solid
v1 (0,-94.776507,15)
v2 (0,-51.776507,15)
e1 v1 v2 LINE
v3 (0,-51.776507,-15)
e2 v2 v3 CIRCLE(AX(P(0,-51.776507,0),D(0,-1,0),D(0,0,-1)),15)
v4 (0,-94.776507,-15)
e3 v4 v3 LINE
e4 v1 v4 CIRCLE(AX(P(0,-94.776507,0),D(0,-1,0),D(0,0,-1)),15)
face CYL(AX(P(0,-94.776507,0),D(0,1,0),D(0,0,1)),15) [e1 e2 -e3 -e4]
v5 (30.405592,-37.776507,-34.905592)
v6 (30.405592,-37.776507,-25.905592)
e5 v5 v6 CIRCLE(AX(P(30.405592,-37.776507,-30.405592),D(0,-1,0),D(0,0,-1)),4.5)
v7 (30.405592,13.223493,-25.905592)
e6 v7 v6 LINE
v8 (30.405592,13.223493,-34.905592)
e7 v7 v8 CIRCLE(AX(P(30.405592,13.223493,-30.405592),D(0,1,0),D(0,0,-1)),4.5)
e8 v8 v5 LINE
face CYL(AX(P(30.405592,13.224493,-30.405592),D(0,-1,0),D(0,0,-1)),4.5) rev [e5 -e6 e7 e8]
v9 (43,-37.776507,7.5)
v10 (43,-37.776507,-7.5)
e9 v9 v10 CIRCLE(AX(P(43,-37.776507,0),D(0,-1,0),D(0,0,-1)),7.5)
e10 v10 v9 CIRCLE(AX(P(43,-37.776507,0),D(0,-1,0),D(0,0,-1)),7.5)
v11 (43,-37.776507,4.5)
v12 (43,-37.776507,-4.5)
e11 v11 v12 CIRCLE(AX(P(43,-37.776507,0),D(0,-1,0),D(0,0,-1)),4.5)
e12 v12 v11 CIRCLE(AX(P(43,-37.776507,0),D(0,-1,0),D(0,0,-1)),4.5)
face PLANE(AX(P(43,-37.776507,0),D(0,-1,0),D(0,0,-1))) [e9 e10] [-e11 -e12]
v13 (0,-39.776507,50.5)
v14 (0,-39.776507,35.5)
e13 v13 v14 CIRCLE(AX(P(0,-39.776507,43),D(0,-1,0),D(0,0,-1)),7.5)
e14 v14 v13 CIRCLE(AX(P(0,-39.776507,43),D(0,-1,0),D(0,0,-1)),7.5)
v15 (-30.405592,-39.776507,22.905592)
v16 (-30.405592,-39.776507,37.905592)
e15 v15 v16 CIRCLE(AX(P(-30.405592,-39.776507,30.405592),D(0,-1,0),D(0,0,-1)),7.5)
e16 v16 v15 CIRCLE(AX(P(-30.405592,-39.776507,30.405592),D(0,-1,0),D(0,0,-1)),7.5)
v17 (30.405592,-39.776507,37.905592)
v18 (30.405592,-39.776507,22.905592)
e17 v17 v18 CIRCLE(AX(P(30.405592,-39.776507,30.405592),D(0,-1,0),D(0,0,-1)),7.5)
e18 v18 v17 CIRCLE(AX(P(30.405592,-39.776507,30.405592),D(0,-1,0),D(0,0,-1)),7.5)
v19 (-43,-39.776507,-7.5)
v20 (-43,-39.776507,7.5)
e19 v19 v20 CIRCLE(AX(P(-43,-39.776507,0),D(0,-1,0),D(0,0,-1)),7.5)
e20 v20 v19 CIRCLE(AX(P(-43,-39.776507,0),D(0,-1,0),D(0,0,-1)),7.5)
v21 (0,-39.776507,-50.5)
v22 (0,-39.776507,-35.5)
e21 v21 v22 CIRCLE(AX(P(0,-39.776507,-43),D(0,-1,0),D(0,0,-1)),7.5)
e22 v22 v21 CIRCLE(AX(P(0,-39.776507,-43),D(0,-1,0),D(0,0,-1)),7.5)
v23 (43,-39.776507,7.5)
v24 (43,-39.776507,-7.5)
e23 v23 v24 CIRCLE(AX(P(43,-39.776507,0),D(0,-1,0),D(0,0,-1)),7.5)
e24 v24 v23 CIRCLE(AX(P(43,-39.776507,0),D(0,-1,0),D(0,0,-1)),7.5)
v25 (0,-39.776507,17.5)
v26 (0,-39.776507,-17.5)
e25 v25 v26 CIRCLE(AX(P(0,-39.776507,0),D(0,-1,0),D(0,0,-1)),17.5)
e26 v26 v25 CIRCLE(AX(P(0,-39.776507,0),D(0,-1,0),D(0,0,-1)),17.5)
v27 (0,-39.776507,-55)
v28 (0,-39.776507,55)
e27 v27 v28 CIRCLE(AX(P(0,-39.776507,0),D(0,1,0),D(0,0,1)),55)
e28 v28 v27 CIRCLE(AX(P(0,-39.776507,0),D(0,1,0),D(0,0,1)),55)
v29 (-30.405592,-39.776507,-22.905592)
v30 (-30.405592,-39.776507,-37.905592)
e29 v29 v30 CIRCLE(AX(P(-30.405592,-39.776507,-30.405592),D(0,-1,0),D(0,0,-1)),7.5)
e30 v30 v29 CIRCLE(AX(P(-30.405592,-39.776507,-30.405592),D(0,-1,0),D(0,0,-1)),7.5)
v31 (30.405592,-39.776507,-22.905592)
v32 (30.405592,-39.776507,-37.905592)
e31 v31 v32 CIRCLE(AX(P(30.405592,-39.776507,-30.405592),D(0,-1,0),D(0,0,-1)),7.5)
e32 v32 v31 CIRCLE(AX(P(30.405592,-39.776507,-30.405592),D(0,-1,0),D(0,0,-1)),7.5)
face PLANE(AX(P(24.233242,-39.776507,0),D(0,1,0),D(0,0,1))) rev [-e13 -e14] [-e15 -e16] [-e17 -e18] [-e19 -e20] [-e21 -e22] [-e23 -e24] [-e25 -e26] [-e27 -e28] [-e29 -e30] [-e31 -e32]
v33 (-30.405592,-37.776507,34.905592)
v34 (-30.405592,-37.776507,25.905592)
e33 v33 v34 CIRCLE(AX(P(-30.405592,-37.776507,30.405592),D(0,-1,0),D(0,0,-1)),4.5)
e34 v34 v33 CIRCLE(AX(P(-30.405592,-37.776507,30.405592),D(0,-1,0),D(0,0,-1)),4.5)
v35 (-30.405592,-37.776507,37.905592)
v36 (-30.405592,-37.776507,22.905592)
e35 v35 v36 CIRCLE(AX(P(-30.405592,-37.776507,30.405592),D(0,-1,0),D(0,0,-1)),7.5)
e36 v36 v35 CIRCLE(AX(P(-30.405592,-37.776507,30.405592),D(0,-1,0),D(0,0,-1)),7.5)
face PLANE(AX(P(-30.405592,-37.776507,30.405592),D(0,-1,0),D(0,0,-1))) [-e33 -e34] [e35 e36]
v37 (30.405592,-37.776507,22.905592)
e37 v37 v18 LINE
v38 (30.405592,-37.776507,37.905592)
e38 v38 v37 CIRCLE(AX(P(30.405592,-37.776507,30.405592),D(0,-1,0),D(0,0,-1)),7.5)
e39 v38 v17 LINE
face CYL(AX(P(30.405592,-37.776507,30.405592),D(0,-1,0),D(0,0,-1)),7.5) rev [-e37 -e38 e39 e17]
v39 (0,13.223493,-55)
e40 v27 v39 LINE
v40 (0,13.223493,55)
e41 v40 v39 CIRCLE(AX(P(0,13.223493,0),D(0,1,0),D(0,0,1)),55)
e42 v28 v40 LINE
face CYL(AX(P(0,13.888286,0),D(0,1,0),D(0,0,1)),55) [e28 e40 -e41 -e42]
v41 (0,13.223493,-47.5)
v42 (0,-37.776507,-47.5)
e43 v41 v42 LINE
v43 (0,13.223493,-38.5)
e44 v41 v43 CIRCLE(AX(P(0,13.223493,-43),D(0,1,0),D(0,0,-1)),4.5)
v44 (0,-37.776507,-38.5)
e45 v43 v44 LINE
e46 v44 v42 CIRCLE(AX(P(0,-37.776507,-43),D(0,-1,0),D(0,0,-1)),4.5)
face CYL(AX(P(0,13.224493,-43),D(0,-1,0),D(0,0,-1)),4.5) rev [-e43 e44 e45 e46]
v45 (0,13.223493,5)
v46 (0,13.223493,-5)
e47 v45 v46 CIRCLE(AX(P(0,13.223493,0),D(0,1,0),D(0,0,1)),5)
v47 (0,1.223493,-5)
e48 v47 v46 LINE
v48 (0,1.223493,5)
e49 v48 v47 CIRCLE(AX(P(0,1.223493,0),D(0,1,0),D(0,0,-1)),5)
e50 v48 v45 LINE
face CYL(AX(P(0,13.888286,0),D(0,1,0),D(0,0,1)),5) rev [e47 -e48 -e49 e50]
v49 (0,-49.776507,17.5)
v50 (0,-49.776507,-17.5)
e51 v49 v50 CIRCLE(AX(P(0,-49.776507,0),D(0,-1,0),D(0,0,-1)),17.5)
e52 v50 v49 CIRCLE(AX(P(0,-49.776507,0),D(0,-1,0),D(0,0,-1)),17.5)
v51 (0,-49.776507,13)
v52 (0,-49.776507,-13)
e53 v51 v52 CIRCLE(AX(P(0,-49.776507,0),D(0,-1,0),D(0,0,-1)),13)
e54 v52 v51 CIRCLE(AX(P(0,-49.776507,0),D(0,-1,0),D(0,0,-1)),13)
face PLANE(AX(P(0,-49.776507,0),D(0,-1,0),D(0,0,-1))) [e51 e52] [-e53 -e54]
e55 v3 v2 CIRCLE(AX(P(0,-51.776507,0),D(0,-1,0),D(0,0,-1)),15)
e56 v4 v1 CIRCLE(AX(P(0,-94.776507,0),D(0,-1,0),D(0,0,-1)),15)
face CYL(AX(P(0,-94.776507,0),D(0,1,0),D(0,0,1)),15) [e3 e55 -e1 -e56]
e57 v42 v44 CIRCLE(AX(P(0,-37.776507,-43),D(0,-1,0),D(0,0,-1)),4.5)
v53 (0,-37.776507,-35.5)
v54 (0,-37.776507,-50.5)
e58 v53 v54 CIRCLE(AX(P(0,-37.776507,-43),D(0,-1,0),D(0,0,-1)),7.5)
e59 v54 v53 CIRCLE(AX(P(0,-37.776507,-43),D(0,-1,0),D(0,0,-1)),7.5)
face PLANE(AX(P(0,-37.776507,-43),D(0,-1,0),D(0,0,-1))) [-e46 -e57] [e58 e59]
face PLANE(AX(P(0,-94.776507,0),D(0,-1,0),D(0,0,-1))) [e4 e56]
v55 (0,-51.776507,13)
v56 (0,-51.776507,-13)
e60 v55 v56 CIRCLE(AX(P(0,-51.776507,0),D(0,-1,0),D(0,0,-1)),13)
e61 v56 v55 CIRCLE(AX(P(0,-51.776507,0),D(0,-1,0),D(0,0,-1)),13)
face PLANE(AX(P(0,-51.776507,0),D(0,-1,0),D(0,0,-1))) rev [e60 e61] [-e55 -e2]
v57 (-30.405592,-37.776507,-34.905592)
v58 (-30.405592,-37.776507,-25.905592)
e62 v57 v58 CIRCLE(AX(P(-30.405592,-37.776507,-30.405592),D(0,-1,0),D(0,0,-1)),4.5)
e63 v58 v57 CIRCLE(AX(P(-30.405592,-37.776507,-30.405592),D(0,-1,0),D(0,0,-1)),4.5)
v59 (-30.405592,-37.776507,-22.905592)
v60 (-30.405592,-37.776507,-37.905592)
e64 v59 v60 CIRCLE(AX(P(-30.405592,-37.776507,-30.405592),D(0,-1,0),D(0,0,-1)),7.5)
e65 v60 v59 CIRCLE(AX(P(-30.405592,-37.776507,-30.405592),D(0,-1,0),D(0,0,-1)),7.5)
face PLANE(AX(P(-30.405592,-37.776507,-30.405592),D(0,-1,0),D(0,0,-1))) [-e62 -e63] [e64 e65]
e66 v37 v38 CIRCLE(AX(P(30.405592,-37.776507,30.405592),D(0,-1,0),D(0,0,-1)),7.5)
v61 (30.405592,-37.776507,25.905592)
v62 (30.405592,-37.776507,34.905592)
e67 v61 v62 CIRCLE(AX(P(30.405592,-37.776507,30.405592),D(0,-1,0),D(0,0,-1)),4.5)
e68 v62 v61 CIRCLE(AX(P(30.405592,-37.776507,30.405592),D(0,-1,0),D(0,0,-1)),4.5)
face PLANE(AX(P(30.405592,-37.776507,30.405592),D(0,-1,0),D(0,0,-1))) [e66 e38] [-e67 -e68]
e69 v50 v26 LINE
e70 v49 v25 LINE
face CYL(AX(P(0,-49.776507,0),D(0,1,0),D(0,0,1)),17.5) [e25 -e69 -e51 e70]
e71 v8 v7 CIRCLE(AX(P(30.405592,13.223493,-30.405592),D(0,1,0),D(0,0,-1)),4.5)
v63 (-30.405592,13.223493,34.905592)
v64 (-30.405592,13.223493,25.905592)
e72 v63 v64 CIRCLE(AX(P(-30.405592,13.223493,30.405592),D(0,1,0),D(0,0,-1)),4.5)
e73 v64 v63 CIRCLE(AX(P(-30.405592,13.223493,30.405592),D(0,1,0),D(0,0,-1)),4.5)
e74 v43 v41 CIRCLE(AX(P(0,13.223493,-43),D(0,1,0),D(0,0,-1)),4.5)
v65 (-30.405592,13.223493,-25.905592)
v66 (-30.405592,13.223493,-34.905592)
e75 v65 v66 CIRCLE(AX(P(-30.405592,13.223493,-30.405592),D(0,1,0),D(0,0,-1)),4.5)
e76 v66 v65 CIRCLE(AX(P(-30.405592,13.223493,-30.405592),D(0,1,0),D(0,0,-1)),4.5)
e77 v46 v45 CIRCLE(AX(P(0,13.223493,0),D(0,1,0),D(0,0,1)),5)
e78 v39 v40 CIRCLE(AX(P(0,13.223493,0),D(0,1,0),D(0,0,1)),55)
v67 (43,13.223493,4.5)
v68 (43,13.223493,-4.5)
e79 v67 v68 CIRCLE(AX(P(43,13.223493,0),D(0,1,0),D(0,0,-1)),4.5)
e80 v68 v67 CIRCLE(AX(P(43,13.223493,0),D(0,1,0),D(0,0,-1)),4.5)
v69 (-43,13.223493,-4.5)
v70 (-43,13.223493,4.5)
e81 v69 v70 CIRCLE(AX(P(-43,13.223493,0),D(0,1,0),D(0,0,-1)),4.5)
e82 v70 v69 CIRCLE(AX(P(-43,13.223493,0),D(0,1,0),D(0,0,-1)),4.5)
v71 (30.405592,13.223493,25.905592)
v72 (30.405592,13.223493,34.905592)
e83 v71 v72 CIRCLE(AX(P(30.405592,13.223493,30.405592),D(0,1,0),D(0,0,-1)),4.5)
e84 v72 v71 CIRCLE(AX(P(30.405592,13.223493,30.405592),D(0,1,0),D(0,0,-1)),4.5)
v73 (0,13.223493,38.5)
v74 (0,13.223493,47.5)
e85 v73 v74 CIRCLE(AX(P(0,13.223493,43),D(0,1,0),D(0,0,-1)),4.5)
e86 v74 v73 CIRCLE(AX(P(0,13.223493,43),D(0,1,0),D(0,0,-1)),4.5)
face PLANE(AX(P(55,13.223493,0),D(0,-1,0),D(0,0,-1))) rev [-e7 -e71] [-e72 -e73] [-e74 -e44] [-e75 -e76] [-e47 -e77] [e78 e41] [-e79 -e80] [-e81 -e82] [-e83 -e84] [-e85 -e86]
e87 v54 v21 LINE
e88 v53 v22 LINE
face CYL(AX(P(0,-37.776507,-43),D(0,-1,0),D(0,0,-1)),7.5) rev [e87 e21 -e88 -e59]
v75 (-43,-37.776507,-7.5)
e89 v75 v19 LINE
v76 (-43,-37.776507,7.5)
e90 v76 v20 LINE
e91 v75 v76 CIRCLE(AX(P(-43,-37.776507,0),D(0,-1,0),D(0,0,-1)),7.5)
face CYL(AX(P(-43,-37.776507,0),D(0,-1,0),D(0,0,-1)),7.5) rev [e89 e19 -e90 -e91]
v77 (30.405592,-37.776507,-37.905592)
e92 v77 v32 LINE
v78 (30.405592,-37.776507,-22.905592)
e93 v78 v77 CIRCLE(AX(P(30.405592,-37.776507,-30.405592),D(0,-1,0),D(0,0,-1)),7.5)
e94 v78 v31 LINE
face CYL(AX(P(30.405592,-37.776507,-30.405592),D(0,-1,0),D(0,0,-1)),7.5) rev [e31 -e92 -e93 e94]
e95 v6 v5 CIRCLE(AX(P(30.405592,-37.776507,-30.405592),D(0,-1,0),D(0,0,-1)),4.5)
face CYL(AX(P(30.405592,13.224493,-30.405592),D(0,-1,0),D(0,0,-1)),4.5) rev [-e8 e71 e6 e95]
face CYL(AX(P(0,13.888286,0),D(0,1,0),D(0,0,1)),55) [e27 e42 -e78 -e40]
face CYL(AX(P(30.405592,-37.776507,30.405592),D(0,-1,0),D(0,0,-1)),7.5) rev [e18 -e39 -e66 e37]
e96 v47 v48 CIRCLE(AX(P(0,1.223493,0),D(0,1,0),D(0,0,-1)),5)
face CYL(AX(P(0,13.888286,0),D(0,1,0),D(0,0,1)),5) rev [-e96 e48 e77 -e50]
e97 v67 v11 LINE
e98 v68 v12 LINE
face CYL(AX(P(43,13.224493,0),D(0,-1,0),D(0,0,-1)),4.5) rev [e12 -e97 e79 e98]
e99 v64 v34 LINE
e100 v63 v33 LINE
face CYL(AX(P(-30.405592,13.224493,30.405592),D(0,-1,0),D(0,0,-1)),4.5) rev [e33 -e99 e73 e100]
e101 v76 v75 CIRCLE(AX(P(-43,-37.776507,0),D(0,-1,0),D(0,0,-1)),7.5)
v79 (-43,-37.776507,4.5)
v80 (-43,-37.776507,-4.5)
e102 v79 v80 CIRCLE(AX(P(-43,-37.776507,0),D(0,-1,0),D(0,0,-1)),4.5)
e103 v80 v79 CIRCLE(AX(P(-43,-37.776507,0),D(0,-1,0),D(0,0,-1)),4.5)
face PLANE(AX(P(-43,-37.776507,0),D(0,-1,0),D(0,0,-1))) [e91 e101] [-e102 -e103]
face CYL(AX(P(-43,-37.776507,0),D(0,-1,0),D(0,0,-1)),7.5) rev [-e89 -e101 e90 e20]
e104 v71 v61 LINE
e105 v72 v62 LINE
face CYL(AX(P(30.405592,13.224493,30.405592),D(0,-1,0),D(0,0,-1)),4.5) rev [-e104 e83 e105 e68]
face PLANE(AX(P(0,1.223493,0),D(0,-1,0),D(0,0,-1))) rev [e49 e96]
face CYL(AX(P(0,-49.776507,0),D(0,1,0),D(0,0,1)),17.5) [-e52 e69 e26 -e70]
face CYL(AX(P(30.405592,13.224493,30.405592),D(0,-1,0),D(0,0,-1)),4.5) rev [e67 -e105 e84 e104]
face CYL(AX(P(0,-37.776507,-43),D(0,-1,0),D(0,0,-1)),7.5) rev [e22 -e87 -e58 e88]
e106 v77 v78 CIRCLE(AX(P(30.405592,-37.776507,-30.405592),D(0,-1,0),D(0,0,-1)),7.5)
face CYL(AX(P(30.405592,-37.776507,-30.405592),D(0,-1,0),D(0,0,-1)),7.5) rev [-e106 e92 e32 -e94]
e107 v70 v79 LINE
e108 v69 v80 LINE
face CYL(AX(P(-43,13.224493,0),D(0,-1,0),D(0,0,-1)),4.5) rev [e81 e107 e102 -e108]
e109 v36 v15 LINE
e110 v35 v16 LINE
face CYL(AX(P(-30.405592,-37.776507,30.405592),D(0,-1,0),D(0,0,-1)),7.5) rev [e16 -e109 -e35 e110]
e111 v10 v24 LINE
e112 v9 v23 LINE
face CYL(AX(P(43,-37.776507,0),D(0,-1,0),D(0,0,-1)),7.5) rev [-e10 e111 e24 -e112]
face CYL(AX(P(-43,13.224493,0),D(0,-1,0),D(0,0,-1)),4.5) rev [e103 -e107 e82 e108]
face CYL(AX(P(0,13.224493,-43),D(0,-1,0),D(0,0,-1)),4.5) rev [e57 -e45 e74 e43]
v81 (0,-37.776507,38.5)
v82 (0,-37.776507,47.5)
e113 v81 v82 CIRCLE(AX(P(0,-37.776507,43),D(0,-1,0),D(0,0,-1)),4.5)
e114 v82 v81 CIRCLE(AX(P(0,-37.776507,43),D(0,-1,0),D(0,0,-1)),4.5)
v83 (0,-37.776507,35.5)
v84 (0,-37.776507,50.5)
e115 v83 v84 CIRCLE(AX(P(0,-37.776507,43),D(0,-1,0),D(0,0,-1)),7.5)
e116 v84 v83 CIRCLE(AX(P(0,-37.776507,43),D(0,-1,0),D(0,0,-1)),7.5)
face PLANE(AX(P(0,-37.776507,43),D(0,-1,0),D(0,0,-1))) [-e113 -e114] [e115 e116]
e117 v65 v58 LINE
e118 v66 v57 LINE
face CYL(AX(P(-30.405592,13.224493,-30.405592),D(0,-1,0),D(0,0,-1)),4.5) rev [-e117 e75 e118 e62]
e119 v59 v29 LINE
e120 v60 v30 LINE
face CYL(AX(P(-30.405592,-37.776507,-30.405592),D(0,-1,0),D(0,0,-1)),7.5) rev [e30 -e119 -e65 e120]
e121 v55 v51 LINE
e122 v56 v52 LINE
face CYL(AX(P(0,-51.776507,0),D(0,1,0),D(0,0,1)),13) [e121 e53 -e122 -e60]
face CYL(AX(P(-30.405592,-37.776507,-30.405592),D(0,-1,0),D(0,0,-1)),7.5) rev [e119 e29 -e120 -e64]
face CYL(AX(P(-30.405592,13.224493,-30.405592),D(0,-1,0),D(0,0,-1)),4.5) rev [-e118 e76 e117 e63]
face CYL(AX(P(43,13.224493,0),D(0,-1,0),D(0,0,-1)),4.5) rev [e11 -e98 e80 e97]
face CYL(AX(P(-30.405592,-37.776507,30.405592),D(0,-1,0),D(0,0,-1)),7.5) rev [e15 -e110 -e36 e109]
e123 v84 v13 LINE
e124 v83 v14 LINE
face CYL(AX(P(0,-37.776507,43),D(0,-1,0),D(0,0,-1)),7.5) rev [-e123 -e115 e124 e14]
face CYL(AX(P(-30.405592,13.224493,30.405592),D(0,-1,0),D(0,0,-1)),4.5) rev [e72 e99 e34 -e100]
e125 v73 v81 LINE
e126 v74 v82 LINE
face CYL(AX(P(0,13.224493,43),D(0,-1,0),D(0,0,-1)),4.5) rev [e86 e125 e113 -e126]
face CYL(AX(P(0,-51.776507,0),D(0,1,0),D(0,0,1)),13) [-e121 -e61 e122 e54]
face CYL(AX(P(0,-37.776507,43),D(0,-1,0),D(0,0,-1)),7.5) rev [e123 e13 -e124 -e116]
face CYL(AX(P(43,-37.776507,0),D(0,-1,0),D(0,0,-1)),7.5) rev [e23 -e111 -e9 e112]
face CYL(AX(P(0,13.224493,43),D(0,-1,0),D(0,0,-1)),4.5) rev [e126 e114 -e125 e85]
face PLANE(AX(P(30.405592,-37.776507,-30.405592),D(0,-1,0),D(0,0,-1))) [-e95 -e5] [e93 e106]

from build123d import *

# Parameters (mm, degrees)
SKETCH_2_R          = 7.5
CUT_EXTRUDE_1_DEPTH = 2
CUT_EXTRUDE_2_REACH = 95.011
SKETCH_5_R          = 4.5
SKETCH_7_R          = 30.721623485
EXTRUDE_1_DEPTH     = 41
SKETCH_8_R          = 17.5
EXTRUDE_2_DEPTH     = 10
SKETCH_9_R          = 15
EXTRUDE_3_DEPTH     = 45
SKETCH_10_R         = 15
SKETCH_10_R_2       = 13
CUT_EXTRUDE_3_DEPTH = 2


with BuildPart() as part:
    # 草图1 → 旋转1 (revolve)
    with BuildSketch(Plane.XY, mode=Mode.PRIVATE) as revolve_1_sk:
        with BuildLine():
            Line((5, 13.223493336), (5, 0.265127902))
            ThreePointArc((5, 0.265127902), (24.788681465, -14.86973249), (24.233241632, -39.776506664))
            Line((24.233241632, -39.776506664), (55, -39.776506664))
            Line((55, -39.776506664), (55, 13.223493336))
            Line((55, 13.223493336), (5, 13.223493336))
        make_face()
    revolve(revolve_1_sk.sketch.rotate(Axis((0, 13.888286008, 0), (0, -1, 0)), 90), axis=Axis((0, 13.888286008, 0), (0, -1, 0)))

    # 草图2 → 切除-拉伸1 (cut)
    with BuildSketch(Plane.XZ.offset(39.776506664)):
        with Locations(Location((43, 0, 0), (0, 0, 270))):
            Circle(SKETCH_2_R)
        with Locations(Location((30.405591591, -30.405591591, 0), (0, 0, 270))):
            Circle(SKETCH_2_R)
        with Locations(Location((0, -43, 0), (0, 0, 270))):
            Circle(SKETCH_2_R)
        with Locations(Location((-30.405591591, -30.405591591, 0), (0, 0, 270))):
            Circle(SKETCH_2_R)
        with Locations(Location((-43, 0, 0), (0, 0, 270))):
            Circle(SKETCH_2_R)
        with Locations(Location((-30.405591591, 30.405591591, 0), (0, 0, 270))):
            Circle(SKETCH_2_R)
        with Locations(Location((0, 43, 0), (0, 0, 270))):
            Circle(SKETCH_2_R)
        with Locations(Location((30.405591591, 30.405591591, 0), (0, 0, 270))):
            Circle(SKETCH_2_R)
    extrude(amount=-CUT_EXTRUDE_1_DEPTH, mode=Mode.SUBTRACT)

    # 草图5 → 切除-拉伸2 (cut, up to next)
    with BuildSketch(Plane.XZ.offset(37.776506664), mode=Mode.PRIVATE) as cut_extrude_2_sk1:
        with Locations(Location((0, 43, 0), (0, 0, 270))):
            Circle(SKETCH_5_R)
    cut_extrude_2_tool1 = extrude(cut_extrude_2_sk1.sketch, amount=-CUT_EXTRUDE_2_REACH, mode=Mode.PRIVATE) & part.part
    # 草图5 → 切除-拉伸2 (cut, up to next)
    with BuildSketch(Plane.XZ.offset(37.776506664), mode=Mode.PRIVATE) as cut_extrude_2_sk2:
        with Locations(Location((30.405591591, 30.405591591, 0), (0, 0, 270))):
            Circle(SKETCH_5_R)
    cut_extrude_2_tool2 = extrude(cut_extrude_2_sk2.sketch, amount=-CUT_EXTRUDE_2_REACH, mode=Mode.PRIVATE) & part.part
    # 草图5 → 切除-拉伸2 (cut, up to next)
    with BuildSketch(Plane.XZ.offset(37.776506664), mode=Mode.PRIVATE) as cut_extrude_2_sk3:
        with Locations(Location((43, 0, 0), (0, 0, 270))):
            Circle(SKETCH_5_R)
    cut_extrude_2_tool3 = extrude(cut_extrude_2_sk3.sketch, amount=-CUT_EXTRUDE_2_REACH, mode=Mode.PRIVATE) & part.part
    # 草图5 → 切除-拉伸2 (cut, up to next)
    with BuildSketch(Plane.XZ.offset(37.776506664), mode=Mode.PRIVATE) as cut_extrude_2_sk4:
        with Locations(Location((30.405591591, -30.405591591, 0), (0, 0, 270))):
            Circle(SKETCH_5_R)
    cut_extrude_2_tool4 = extrude(cut_extrude_2_sk4.sketch, amount=-CUT_EXTRUDE_2_REACH, mode=Mode.PRIVATE) & part.part
    # 草图5 → 切除-拉伸2 (cut, up to next)
    with BuildSketch(Plane.XZ.offset(37.776506664), mode=Mode.PRIVATE) as cut_extrude_2_sk5:
        with Locations(Location((0, -43, 0), (0, 0, 270))):
            Circle(SKETCH_5_R)
    cut_extrude_2_tool5 = extrude(cut_extrude_2_sk5.sketch, amount=-CUT_EXTRUDE_2_REACH, mode=Mode.PRIVATE) & part.part
    # 草图5 → 切除-拉伸2 (cut, up to next)
    with BuildSketch(Plane.XZ.offset(37.776506664), mode=Mode.PRIVATE) as cut_extrude_2_sk6:
        with Locations(Location((-30.405591591, -30.405591591, 0), (0, 0, 270))):
            Circle(SKETCH_5_R)
    cut_extrude_2_tool6 = extrude(cut_extrude_2_sk6.sketch, amount=-CUT_EXTRUDE_2_REACH, mode=Mode.PRIVATE) & part.part
    # 草图5 → 切除-拉伸2 (cut, up to next)
    with BuildSketch(Plane.XZ.offset(37.776506664), mode=Mode.PRIVATE) as cut_extrude_2_sk7:
        with Locations(Location((-43, 0, 0), (0, 0, 270))):
            Circle(SKETCH_5_R)
    cut_extrude_2_tool7 = extrude(cut_extrude_2_sk7.sketch, amount=-CUT_EXTRUDE_2_REACH, mode=Mode.PRIVATE) & part.part
    # 草图5 → 切除-拉伸2 (cut, up to next)
    with BuildSketch(Plane.XZ.offset(37.776506664), mode=Mode.PRIVATE) as cut_extrude_2_sk8:
        with Locations(Location((-30.405591591, 30.405591591, 0), (0, 0, 270))):
            Circle(SKETCH_5_R)
    cut_extrude_2_tool8 = extrude(cut_extrude_2_sk8.sketch, amount=-CUT_EXTRUDE_2_REACH, mode=Mode.PRIVATE) & part.part
    add(cut_extrude_2_tool1.solids().sort_by_distance((0, -37.776507, 43))[0], mode=Mode.SUBTRACT)
    add(cut_extrude_2_tool2.solids().sort_by_distance((30.405592, -37.776507, 30.405592))[0], mode=Mode.SUBTRACT)
    add(cut_extrude_2_tool3.solids().sort_by_distance((43, -37.776507, 0))[0], mode=Mode.SUBTRACT)
    add(cut_extrude_2_tool4.solids().sort_by_distance((30.405592, -37.776507, -30.405592))[0], mode=Mode.SUBTRACT)
    add(cut_extrude_2_tool5.solids().sort_by_distance((0, -37.776507, -43))[0], mode=Mode.SUBTRACT)
    add(cut_extrude_2_tool6.solids().sort_by_distance((-30.405592, -37.776507, -30.405592))[0], mode=Mode.SUBTRACT)
    add(cut_extrude_2_tool7.solids().sort_by_distance((-43, -37.776507, 0))[0], mode=Mode.SUBTRACT)
    add(cut_extrude_2_tool8.solids().sort_by_distance((-30.405592, -37.776507, 30.405592))[0], mode=Mode.SUBTRACT)

    # 草图7 → 凸台-拉伸1 (add)
    with BuildSketch(Plane.XZ.offset(39.776506664)):
        Circle(SKETCH_7_R)
    extrude(amount=-EXTRUDE_1_DEPTH)

    # 草图8 → 凸台-拉伸2 (add)
    with BuildSketch(Plane.XZ.offset(39.776506664)):
        with Locations(Location((0, 0, 0), (0, 0, 270))):
            Circle(SKETCH_8_R)
    extrude(amount=EXTRUDE_2_DEPTH)

    # 草图9 → 凸台-拉伸3 (add)
    with BuildSketch(Plane.XZ.offset(49.776506664)):
        with Locations(Location((0, 0, 0), (0, 0, 90))):
            Circle(SKETCH_9_R)
    extrude(amount=EXTRUDE_3_DEPTH)

    # 草图10 → 切除-拉伸3 (cut)
    with BuildSketch(Plane.XZ.offset(49.776506664)):
        with Locations(Location((0, 0, 0), (0, 0, 90))):
            Circle(SKETCH_10_R)
        with Locations(Location((0, 0, 0), (0, 0, 270))):
            Circle(SKETCH_10_R_2, mode=Mode.SUBTRACT)
    extrude(amount=CUT_EXTRUDE_3_DEPTH, mode=Mode.SUBTRACT)


solid = part.part
